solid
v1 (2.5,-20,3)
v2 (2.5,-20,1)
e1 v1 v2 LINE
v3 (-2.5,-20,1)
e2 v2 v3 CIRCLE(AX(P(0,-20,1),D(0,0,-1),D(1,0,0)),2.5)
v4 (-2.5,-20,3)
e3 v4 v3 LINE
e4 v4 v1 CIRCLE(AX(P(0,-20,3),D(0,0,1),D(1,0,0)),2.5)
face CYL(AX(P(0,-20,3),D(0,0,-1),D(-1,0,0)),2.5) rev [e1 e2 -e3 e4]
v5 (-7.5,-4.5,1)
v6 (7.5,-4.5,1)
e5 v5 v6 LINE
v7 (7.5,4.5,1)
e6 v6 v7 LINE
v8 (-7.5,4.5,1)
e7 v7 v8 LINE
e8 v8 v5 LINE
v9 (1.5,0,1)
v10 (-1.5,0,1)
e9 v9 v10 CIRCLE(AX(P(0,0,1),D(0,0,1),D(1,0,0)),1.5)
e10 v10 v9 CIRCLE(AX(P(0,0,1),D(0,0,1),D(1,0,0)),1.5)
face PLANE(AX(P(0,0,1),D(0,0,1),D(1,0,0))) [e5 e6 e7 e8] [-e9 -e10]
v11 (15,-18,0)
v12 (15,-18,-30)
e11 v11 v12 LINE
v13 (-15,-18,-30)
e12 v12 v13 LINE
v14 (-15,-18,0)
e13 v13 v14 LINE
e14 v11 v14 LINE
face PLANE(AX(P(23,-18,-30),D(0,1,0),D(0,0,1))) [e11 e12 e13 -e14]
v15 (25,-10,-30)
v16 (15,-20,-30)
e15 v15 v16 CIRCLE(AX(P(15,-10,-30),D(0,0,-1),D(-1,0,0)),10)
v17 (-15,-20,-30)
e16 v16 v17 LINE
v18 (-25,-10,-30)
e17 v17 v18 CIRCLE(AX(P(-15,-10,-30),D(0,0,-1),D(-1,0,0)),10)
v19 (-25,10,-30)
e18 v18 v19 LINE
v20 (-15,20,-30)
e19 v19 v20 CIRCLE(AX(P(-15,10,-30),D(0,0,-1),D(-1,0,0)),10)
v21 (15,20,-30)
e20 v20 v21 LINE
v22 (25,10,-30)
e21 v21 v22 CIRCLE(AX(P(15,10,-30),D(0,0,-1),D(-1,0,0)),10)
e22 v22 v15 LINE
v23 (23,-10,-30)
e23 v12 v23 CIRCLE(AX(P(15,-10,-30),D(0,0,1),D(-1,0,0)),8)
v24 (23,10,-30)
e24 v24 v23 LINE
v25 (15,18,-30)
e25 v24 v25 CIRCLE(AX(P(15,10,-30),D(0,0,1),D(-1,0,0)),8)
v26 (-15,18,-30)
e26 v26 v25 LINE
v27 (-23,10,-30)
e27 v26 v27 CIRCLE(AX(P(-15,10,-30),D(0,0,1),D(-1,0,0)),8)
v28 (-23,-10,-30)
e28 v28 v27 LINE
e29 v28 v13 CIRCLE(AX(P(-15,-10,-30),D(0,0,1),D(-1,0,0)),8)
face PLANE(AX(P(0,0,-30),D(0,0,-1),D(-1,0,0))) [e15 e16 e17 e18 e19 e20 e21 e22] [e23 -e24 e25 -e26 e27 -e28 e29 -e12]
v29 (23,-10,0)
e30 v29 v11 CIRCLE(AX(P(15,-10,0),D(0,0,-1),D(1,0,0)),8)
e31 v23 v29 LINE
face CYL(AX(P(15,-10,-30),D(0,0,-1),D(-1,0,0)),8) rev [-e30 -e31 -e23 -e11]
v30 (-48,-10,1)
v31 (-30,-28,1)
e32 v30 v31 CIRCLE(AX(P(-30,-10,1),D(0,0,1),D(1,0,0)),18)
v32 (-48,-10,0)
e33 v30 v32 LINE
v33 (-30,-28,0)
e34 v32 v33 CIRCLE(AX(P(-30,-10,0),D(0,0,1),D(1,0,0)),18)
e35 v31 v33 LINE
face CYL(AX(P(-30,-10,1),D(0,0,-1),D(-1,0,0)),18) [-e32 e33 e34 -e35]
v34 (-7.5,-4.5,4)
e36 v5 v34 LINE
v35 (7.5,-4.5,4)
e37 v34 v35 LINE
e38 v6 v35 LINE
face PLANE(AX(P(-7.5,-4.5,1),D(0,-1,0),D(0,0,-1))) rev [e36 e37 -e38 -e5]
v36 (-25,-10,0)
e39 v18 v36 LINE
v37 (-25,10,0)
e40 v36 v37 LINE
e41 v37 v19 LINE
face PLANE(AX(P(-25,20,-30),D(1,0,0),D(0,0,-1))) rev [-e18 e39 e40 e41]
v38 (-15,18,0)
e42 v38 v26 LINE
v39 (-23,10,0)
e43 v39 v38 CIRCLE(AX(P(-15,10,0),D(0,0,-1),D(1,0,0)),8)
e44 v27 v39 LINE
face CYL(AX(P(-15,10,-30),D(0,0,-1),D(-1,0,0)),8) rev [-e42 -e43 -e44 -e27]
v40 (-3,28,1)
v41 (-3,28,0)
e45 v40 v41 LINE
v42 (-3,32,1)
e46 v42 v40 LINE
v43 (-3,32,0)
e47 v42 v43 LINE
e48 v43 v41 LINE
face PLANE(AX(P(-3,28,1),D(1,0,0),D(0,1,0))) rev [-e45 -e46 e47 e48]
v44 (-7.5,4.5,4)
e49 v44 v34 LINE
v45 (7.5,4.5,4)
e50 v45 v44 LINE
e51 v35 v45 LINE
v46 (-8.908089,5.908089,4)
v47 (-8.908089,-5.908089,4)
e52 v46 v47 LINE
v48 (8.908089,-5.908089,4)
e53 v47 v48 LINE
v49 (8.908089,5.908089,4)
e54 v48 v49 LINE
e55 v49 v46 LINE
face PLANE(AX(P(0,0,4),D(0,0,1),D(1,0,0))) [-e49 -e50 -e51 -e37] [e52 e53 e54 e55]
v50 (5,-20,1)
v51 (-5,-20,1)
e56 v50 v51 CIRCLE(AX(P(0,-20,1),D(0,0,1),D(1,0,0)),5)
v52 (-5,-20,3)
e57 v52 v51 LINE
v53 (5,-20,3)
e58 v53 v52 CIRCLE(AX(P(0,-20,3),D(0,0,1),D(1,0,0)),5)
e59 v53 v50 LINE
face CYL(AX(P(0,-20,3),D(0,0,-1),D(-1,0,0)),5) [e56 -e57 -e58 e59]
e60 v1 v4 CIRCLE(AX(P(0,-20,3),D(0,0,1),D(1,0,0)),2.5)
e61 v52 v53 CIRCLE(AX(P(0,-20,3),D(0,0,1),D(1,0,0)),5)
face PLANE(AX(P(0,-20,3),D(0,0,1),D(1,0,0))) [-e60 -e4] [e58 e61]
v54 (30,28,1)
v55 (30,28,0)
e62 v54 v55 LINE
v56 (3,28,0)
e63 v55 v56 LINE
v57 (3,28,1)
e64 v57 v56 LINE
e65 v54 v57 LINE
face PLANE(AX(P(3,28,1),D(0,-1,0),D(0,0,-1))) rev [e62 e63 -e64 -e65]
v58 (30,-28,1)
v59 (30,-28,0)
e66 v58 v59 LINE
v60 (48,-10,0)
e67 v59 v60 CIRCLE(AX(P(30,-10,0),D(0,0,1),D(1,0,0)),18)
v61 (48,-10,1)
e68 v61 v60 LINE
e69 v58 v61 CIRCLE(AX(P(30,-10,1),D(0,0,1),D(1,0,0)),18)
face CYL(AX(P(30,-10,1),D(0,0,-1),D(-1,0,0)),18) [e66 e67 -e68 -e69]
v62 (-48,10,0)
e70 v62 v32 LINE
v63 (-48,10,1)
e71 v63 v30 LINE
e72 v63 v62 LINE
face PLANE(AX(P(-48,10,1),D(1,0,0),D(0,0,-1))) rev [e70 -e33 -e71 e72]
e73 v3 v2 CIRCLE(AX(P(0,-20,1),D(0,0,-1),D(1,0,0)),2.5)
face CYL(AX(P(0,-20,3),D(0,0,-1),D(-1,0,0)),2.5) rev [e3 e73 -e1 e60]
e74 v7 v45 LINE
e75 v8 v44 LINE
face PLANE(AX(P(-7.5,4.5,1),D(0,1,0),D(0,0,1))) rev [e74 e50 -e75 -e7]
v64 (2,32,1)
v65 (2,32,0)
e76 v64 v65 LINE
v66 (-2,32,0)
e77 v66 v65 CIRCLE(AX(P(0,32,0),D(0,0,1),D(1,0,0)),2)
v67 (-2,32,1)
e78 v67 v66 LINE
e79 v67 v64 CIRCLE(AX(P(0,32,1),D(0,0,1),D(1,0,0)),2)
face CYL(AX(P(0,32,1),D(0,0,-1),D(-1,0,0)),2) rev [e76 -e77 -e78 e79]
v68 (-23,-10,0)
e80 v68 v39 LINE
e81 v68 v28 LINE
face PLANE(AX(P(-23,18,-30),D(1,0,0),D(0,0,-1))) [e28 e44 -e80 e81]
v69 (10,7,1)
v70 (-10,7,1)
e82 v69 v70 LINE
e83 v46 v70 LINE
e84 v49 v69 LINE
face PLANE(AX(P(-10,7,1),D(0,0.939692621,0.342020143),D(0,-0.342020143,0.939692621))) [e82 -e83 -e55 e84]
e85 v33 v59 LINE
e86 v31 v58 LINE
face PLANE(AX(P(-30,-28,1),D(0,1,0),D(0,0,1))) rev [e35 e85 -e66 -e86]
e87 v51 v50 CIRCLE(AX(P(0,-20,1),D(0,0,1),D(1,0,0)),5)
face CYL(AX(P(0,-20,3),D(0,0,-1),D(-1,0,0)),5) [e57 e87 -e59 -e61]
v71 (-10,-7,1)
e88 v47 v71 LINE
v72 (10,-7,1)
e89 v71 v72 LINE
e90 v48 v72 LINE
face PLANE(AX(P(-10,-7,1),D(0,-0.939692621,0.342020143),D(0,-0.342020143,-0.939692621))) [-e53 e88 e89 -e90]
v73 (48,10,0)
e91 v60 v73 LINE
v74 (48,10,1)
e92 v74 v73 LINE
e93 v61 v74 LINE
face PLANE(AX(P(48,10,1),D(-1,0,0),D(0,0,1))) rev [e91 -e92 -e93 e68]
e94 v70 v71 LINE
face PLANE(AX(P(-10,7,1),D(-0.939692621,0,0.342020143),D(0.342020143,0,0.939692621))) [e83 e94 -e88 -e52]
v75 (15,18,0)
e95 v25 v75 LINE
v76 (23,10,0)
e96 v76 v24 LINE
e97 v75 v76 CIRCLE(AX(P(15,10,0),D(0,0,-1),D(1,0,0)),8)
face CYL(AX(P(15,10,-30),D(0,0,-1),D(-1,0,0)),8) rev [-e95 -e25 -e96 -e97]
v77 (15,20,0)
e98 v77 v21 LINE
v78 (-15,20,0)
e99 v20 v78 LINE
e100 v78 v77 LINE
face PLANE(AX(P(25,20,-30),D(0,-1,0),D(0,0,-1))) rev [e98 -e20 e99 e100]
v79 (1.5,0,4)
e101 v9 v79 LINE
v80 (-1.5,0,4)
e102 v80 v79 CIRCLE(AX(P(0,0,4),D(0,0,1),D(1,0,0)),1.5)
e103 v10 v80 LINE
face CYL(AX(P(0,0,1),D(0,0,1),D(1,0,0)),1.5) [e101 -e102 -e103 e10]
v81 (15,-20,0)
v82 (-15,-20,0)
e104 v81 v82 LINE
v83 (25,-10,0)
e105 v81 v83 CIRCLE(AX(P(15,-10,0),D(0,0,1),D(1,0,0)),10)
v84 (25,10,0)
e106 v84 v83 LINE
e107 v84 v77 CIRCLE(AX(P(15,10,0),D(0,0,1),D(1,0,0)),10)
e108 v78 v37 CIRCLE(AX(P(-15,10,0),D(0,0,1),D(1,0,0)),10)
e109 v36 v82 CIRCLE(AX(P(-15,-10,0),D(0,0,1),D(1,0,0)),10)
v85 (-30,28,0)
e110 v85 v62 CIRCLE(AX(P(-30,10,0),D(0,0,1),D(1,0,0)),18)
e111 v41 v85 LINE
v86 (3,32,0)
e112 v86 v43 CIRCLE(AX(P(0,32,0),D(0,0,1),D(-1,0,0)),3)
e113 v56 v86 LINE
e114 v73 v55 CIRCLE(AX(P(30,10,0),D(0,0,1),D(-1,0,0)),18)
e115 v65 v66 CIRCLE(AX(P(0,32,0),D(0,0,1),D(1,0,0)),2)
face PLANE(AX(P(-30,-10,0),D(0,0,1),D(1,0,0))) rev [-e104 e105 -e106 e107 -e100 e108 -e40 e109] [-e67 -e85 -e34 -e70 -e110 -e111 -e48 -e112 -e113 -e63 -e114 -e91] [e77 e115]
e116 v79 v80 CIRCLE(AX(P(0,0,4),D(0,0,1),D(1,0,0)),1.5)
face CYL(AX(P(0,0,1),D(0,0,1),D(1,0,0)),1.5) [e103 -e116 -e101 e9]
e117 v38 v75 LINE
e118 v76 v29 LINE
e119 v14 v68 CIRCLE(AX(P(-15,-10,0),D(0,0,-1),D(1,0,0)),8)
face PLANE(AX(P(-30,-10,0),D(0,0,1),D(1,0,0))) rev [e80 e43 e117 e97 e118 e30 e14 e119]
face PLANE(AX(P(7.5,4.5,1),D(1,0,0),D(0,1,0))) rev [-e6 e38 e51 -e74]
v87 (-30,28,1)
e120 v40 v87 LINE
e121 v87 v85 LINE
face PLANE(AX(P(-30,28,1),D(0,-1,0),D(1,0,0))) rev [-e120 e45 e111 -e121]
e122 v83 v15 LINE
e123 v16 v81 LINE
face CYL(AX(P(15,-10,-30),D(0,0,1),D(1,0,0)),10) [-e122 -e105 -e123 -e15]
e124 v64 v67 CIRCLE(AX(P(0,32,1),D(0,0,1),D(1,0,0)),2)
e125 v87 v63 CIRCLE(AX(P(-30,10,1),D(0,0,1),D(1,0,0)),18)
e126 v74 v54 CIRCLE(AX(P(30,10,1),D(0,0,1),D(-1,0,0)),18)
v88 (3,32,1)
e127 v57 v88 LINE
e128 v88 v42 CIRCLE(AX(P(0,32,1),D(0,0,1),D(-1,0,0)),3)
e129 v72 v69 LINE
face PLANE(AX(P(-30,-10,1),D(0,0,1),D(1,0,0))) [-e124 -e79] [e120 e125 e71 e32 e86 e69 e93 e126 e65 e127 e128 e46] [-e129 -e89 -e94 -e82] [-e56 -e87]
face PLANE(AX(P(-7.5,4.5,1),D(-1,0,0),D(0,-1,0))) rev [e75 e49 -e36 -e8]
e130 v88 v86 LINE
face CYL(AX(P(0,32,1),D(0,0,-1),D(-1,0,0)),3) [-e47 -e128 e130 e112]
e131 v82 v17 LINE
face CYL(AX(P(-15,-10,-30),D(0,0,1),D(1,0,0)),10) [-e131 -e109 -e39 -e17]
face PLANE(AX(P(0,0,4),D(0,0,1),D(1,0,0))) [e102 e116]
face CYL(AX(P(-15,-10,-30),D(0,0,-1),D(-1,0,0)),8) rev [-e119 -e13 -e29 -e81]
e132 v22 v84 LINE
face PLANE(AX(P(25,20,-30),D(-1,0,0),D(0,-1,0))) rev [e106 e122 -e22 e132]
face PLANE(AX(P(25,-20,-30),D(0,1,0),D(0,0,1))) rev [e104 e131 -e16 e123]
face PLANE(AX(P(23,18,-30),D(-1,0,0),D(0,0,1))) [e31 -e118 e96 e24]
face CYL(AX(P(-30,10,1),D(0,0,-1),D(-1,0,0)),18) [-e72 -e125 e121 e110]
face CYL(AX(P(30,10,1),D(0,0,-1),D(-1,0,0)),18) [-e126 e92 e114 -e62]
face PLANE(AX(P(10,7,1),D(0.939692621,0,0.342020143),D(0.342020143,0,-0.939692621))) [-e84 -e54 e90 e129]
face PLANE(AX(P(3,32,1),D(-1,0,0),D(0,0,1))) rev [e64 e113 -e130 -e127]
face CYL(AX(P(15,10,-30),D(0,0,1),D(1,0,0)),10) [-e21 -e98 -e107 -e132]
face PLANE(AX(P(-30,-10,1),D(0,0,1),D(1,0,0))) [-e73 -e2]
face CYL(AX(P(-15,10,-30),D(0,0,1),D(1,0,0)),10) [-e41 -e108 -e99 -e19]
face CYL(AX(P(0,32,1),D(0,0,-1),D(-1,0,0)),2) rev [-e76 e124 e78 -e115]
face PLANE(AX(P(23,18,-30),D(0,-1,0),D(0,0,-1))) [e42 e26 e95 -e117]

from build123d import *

# Parameters (mm, degrees)
SKETCH1_R           = 2
BOSS_EXTRUDE1_DEPTH = 1
SKETCH2_W           = 20
SKETCH2_H           = 14
BOSS_EXTRUDE2_DEPTH = 3
BOSS_EXTRUDE2_TAPER = 20
SKETCH3_W           = 15
SKETCH3_H           = 9
SKETCH3_R           = 1.5
CUT_EXTRUDE1_DEPTH  = 3
SKETCH4_W           = 50
SKETCH4_H           = 40
SKETCH4_W_2         = 46
SKETCH4_H_2         = 36
BOSS_EXTRUDE3_DEPTH = 30
SKETCH5_R           = 5
SKETCH5_R_2         = 2.5
BOSS_EXTRUDE4_DEPTH = 2
FILLET1_R           = 8
FILLET2_R           = 10


with BuildPart() as part:
    # Sketch1 → Boss-Extrude1 (new body)
    with BuildSketch(Plane.XY):
        with BuildLine():
            Line((-3, 28), (-3, 32))
            ThreePointArc((-3, 32), (0, 35), (3, 32))
            Line((3, 32), (3, 28))
            Line((3, 28), (30, 28))
            ThreePointArc((30, 28), (42.727922061, 22.727922061), (48, 10))
            Line((48, 10), (48, -10))
            ThreePointArc((48, -10), (42.727922061, -22.727922061), (30, -28))
            Line((30, -28), (-30, -28))
            ThreePointArc((-30, -28), (-42.727922061, -22.727922061), (-48, -10))
            Line((-48, -10), (-48, 10))
            ThreePointArc((-48, 10), (-42.727922061, 22.727922061), (-30, 28))
            Line((-30, 28), (-3, 28))
        make_face()
        with Locations((0, 32)):
            Circle(SKETCH1_R, mode=Mode.SUBTRACT)
    extrude(amount=BOSS_EXTRUDE1_DEPTH)

    # Sketch2 → Boss-Extrude2 (add)
    with BuildSketch(Plane.XY.offset(1)):
        Rectangle(SKETCH2_W, SKETCH2_H)
    extrude(amount=BOSS_EXTRUDE2_DEPTH, taper=BOSS_EXTRUDE2_TAPER)

    # Sketch3 → Cut-Extrude1 (cut)
    with BuildSketch(Plane.XY.offset(4)):
        Rectangle(SKETCH3_W, SKETCH3_H)
        Circle(SKETCH3_R, mode=Mode.SUBTRACT)
    extrude(amount=-CUT_EXTRUDE1_DEPTH, mode=Mode.SUBTRACT)

    # Sketch4 → Boss-Extrude3 (add)
    with BuildSketch(Plane(origin=(0, 0, 0), x_dir=(-1, 0, 0), z_dir=(0, 0, -1))):
        Rectangle(SKETCH4_W, SKETCH4_H)
        Rectangle(SKETCH4_W_2, SKETCH4_H_2, mode=Mode.SUBTRACT)
    extrude(amount=BOSS_EXTRUDE3_DEPTH)

    # Sketch5 → Boss-Extrude4 (add)
    with BuildSketch(Plane.XY.offset(1)):
        with Locations((0, -20)):
            Circle(SKETCH5_R)
        with Locations((0, -20)):
            Circle(SKETCH5_R_2, mode=Mode.SUBTRACT)
    extrude(amount=BOSS_EXTRUDE4_DEPTH)

    # Fillet1
    fillet1_edges = [part.edges().sort_by_distance(p)[0] for p in [
        (-23, 18, -15),
        (23, 18, -15),
        (23, -18, -15),
        (-23, -18, -15),
    ]]
    fillet(fillet1_edges, radius=FILLET1_R)

    # Fillet2
    fillet2_edges = [part.edges().sort_by_distance(p)[0] for p in [
        (-25, -20, -15),
        (-25, 20, -15),
        (25, 20, -15),
        (25, -20, -15),
    ]]
    fillet(fillet2_edges, radius=FILLET2_R)


solid = part.part
